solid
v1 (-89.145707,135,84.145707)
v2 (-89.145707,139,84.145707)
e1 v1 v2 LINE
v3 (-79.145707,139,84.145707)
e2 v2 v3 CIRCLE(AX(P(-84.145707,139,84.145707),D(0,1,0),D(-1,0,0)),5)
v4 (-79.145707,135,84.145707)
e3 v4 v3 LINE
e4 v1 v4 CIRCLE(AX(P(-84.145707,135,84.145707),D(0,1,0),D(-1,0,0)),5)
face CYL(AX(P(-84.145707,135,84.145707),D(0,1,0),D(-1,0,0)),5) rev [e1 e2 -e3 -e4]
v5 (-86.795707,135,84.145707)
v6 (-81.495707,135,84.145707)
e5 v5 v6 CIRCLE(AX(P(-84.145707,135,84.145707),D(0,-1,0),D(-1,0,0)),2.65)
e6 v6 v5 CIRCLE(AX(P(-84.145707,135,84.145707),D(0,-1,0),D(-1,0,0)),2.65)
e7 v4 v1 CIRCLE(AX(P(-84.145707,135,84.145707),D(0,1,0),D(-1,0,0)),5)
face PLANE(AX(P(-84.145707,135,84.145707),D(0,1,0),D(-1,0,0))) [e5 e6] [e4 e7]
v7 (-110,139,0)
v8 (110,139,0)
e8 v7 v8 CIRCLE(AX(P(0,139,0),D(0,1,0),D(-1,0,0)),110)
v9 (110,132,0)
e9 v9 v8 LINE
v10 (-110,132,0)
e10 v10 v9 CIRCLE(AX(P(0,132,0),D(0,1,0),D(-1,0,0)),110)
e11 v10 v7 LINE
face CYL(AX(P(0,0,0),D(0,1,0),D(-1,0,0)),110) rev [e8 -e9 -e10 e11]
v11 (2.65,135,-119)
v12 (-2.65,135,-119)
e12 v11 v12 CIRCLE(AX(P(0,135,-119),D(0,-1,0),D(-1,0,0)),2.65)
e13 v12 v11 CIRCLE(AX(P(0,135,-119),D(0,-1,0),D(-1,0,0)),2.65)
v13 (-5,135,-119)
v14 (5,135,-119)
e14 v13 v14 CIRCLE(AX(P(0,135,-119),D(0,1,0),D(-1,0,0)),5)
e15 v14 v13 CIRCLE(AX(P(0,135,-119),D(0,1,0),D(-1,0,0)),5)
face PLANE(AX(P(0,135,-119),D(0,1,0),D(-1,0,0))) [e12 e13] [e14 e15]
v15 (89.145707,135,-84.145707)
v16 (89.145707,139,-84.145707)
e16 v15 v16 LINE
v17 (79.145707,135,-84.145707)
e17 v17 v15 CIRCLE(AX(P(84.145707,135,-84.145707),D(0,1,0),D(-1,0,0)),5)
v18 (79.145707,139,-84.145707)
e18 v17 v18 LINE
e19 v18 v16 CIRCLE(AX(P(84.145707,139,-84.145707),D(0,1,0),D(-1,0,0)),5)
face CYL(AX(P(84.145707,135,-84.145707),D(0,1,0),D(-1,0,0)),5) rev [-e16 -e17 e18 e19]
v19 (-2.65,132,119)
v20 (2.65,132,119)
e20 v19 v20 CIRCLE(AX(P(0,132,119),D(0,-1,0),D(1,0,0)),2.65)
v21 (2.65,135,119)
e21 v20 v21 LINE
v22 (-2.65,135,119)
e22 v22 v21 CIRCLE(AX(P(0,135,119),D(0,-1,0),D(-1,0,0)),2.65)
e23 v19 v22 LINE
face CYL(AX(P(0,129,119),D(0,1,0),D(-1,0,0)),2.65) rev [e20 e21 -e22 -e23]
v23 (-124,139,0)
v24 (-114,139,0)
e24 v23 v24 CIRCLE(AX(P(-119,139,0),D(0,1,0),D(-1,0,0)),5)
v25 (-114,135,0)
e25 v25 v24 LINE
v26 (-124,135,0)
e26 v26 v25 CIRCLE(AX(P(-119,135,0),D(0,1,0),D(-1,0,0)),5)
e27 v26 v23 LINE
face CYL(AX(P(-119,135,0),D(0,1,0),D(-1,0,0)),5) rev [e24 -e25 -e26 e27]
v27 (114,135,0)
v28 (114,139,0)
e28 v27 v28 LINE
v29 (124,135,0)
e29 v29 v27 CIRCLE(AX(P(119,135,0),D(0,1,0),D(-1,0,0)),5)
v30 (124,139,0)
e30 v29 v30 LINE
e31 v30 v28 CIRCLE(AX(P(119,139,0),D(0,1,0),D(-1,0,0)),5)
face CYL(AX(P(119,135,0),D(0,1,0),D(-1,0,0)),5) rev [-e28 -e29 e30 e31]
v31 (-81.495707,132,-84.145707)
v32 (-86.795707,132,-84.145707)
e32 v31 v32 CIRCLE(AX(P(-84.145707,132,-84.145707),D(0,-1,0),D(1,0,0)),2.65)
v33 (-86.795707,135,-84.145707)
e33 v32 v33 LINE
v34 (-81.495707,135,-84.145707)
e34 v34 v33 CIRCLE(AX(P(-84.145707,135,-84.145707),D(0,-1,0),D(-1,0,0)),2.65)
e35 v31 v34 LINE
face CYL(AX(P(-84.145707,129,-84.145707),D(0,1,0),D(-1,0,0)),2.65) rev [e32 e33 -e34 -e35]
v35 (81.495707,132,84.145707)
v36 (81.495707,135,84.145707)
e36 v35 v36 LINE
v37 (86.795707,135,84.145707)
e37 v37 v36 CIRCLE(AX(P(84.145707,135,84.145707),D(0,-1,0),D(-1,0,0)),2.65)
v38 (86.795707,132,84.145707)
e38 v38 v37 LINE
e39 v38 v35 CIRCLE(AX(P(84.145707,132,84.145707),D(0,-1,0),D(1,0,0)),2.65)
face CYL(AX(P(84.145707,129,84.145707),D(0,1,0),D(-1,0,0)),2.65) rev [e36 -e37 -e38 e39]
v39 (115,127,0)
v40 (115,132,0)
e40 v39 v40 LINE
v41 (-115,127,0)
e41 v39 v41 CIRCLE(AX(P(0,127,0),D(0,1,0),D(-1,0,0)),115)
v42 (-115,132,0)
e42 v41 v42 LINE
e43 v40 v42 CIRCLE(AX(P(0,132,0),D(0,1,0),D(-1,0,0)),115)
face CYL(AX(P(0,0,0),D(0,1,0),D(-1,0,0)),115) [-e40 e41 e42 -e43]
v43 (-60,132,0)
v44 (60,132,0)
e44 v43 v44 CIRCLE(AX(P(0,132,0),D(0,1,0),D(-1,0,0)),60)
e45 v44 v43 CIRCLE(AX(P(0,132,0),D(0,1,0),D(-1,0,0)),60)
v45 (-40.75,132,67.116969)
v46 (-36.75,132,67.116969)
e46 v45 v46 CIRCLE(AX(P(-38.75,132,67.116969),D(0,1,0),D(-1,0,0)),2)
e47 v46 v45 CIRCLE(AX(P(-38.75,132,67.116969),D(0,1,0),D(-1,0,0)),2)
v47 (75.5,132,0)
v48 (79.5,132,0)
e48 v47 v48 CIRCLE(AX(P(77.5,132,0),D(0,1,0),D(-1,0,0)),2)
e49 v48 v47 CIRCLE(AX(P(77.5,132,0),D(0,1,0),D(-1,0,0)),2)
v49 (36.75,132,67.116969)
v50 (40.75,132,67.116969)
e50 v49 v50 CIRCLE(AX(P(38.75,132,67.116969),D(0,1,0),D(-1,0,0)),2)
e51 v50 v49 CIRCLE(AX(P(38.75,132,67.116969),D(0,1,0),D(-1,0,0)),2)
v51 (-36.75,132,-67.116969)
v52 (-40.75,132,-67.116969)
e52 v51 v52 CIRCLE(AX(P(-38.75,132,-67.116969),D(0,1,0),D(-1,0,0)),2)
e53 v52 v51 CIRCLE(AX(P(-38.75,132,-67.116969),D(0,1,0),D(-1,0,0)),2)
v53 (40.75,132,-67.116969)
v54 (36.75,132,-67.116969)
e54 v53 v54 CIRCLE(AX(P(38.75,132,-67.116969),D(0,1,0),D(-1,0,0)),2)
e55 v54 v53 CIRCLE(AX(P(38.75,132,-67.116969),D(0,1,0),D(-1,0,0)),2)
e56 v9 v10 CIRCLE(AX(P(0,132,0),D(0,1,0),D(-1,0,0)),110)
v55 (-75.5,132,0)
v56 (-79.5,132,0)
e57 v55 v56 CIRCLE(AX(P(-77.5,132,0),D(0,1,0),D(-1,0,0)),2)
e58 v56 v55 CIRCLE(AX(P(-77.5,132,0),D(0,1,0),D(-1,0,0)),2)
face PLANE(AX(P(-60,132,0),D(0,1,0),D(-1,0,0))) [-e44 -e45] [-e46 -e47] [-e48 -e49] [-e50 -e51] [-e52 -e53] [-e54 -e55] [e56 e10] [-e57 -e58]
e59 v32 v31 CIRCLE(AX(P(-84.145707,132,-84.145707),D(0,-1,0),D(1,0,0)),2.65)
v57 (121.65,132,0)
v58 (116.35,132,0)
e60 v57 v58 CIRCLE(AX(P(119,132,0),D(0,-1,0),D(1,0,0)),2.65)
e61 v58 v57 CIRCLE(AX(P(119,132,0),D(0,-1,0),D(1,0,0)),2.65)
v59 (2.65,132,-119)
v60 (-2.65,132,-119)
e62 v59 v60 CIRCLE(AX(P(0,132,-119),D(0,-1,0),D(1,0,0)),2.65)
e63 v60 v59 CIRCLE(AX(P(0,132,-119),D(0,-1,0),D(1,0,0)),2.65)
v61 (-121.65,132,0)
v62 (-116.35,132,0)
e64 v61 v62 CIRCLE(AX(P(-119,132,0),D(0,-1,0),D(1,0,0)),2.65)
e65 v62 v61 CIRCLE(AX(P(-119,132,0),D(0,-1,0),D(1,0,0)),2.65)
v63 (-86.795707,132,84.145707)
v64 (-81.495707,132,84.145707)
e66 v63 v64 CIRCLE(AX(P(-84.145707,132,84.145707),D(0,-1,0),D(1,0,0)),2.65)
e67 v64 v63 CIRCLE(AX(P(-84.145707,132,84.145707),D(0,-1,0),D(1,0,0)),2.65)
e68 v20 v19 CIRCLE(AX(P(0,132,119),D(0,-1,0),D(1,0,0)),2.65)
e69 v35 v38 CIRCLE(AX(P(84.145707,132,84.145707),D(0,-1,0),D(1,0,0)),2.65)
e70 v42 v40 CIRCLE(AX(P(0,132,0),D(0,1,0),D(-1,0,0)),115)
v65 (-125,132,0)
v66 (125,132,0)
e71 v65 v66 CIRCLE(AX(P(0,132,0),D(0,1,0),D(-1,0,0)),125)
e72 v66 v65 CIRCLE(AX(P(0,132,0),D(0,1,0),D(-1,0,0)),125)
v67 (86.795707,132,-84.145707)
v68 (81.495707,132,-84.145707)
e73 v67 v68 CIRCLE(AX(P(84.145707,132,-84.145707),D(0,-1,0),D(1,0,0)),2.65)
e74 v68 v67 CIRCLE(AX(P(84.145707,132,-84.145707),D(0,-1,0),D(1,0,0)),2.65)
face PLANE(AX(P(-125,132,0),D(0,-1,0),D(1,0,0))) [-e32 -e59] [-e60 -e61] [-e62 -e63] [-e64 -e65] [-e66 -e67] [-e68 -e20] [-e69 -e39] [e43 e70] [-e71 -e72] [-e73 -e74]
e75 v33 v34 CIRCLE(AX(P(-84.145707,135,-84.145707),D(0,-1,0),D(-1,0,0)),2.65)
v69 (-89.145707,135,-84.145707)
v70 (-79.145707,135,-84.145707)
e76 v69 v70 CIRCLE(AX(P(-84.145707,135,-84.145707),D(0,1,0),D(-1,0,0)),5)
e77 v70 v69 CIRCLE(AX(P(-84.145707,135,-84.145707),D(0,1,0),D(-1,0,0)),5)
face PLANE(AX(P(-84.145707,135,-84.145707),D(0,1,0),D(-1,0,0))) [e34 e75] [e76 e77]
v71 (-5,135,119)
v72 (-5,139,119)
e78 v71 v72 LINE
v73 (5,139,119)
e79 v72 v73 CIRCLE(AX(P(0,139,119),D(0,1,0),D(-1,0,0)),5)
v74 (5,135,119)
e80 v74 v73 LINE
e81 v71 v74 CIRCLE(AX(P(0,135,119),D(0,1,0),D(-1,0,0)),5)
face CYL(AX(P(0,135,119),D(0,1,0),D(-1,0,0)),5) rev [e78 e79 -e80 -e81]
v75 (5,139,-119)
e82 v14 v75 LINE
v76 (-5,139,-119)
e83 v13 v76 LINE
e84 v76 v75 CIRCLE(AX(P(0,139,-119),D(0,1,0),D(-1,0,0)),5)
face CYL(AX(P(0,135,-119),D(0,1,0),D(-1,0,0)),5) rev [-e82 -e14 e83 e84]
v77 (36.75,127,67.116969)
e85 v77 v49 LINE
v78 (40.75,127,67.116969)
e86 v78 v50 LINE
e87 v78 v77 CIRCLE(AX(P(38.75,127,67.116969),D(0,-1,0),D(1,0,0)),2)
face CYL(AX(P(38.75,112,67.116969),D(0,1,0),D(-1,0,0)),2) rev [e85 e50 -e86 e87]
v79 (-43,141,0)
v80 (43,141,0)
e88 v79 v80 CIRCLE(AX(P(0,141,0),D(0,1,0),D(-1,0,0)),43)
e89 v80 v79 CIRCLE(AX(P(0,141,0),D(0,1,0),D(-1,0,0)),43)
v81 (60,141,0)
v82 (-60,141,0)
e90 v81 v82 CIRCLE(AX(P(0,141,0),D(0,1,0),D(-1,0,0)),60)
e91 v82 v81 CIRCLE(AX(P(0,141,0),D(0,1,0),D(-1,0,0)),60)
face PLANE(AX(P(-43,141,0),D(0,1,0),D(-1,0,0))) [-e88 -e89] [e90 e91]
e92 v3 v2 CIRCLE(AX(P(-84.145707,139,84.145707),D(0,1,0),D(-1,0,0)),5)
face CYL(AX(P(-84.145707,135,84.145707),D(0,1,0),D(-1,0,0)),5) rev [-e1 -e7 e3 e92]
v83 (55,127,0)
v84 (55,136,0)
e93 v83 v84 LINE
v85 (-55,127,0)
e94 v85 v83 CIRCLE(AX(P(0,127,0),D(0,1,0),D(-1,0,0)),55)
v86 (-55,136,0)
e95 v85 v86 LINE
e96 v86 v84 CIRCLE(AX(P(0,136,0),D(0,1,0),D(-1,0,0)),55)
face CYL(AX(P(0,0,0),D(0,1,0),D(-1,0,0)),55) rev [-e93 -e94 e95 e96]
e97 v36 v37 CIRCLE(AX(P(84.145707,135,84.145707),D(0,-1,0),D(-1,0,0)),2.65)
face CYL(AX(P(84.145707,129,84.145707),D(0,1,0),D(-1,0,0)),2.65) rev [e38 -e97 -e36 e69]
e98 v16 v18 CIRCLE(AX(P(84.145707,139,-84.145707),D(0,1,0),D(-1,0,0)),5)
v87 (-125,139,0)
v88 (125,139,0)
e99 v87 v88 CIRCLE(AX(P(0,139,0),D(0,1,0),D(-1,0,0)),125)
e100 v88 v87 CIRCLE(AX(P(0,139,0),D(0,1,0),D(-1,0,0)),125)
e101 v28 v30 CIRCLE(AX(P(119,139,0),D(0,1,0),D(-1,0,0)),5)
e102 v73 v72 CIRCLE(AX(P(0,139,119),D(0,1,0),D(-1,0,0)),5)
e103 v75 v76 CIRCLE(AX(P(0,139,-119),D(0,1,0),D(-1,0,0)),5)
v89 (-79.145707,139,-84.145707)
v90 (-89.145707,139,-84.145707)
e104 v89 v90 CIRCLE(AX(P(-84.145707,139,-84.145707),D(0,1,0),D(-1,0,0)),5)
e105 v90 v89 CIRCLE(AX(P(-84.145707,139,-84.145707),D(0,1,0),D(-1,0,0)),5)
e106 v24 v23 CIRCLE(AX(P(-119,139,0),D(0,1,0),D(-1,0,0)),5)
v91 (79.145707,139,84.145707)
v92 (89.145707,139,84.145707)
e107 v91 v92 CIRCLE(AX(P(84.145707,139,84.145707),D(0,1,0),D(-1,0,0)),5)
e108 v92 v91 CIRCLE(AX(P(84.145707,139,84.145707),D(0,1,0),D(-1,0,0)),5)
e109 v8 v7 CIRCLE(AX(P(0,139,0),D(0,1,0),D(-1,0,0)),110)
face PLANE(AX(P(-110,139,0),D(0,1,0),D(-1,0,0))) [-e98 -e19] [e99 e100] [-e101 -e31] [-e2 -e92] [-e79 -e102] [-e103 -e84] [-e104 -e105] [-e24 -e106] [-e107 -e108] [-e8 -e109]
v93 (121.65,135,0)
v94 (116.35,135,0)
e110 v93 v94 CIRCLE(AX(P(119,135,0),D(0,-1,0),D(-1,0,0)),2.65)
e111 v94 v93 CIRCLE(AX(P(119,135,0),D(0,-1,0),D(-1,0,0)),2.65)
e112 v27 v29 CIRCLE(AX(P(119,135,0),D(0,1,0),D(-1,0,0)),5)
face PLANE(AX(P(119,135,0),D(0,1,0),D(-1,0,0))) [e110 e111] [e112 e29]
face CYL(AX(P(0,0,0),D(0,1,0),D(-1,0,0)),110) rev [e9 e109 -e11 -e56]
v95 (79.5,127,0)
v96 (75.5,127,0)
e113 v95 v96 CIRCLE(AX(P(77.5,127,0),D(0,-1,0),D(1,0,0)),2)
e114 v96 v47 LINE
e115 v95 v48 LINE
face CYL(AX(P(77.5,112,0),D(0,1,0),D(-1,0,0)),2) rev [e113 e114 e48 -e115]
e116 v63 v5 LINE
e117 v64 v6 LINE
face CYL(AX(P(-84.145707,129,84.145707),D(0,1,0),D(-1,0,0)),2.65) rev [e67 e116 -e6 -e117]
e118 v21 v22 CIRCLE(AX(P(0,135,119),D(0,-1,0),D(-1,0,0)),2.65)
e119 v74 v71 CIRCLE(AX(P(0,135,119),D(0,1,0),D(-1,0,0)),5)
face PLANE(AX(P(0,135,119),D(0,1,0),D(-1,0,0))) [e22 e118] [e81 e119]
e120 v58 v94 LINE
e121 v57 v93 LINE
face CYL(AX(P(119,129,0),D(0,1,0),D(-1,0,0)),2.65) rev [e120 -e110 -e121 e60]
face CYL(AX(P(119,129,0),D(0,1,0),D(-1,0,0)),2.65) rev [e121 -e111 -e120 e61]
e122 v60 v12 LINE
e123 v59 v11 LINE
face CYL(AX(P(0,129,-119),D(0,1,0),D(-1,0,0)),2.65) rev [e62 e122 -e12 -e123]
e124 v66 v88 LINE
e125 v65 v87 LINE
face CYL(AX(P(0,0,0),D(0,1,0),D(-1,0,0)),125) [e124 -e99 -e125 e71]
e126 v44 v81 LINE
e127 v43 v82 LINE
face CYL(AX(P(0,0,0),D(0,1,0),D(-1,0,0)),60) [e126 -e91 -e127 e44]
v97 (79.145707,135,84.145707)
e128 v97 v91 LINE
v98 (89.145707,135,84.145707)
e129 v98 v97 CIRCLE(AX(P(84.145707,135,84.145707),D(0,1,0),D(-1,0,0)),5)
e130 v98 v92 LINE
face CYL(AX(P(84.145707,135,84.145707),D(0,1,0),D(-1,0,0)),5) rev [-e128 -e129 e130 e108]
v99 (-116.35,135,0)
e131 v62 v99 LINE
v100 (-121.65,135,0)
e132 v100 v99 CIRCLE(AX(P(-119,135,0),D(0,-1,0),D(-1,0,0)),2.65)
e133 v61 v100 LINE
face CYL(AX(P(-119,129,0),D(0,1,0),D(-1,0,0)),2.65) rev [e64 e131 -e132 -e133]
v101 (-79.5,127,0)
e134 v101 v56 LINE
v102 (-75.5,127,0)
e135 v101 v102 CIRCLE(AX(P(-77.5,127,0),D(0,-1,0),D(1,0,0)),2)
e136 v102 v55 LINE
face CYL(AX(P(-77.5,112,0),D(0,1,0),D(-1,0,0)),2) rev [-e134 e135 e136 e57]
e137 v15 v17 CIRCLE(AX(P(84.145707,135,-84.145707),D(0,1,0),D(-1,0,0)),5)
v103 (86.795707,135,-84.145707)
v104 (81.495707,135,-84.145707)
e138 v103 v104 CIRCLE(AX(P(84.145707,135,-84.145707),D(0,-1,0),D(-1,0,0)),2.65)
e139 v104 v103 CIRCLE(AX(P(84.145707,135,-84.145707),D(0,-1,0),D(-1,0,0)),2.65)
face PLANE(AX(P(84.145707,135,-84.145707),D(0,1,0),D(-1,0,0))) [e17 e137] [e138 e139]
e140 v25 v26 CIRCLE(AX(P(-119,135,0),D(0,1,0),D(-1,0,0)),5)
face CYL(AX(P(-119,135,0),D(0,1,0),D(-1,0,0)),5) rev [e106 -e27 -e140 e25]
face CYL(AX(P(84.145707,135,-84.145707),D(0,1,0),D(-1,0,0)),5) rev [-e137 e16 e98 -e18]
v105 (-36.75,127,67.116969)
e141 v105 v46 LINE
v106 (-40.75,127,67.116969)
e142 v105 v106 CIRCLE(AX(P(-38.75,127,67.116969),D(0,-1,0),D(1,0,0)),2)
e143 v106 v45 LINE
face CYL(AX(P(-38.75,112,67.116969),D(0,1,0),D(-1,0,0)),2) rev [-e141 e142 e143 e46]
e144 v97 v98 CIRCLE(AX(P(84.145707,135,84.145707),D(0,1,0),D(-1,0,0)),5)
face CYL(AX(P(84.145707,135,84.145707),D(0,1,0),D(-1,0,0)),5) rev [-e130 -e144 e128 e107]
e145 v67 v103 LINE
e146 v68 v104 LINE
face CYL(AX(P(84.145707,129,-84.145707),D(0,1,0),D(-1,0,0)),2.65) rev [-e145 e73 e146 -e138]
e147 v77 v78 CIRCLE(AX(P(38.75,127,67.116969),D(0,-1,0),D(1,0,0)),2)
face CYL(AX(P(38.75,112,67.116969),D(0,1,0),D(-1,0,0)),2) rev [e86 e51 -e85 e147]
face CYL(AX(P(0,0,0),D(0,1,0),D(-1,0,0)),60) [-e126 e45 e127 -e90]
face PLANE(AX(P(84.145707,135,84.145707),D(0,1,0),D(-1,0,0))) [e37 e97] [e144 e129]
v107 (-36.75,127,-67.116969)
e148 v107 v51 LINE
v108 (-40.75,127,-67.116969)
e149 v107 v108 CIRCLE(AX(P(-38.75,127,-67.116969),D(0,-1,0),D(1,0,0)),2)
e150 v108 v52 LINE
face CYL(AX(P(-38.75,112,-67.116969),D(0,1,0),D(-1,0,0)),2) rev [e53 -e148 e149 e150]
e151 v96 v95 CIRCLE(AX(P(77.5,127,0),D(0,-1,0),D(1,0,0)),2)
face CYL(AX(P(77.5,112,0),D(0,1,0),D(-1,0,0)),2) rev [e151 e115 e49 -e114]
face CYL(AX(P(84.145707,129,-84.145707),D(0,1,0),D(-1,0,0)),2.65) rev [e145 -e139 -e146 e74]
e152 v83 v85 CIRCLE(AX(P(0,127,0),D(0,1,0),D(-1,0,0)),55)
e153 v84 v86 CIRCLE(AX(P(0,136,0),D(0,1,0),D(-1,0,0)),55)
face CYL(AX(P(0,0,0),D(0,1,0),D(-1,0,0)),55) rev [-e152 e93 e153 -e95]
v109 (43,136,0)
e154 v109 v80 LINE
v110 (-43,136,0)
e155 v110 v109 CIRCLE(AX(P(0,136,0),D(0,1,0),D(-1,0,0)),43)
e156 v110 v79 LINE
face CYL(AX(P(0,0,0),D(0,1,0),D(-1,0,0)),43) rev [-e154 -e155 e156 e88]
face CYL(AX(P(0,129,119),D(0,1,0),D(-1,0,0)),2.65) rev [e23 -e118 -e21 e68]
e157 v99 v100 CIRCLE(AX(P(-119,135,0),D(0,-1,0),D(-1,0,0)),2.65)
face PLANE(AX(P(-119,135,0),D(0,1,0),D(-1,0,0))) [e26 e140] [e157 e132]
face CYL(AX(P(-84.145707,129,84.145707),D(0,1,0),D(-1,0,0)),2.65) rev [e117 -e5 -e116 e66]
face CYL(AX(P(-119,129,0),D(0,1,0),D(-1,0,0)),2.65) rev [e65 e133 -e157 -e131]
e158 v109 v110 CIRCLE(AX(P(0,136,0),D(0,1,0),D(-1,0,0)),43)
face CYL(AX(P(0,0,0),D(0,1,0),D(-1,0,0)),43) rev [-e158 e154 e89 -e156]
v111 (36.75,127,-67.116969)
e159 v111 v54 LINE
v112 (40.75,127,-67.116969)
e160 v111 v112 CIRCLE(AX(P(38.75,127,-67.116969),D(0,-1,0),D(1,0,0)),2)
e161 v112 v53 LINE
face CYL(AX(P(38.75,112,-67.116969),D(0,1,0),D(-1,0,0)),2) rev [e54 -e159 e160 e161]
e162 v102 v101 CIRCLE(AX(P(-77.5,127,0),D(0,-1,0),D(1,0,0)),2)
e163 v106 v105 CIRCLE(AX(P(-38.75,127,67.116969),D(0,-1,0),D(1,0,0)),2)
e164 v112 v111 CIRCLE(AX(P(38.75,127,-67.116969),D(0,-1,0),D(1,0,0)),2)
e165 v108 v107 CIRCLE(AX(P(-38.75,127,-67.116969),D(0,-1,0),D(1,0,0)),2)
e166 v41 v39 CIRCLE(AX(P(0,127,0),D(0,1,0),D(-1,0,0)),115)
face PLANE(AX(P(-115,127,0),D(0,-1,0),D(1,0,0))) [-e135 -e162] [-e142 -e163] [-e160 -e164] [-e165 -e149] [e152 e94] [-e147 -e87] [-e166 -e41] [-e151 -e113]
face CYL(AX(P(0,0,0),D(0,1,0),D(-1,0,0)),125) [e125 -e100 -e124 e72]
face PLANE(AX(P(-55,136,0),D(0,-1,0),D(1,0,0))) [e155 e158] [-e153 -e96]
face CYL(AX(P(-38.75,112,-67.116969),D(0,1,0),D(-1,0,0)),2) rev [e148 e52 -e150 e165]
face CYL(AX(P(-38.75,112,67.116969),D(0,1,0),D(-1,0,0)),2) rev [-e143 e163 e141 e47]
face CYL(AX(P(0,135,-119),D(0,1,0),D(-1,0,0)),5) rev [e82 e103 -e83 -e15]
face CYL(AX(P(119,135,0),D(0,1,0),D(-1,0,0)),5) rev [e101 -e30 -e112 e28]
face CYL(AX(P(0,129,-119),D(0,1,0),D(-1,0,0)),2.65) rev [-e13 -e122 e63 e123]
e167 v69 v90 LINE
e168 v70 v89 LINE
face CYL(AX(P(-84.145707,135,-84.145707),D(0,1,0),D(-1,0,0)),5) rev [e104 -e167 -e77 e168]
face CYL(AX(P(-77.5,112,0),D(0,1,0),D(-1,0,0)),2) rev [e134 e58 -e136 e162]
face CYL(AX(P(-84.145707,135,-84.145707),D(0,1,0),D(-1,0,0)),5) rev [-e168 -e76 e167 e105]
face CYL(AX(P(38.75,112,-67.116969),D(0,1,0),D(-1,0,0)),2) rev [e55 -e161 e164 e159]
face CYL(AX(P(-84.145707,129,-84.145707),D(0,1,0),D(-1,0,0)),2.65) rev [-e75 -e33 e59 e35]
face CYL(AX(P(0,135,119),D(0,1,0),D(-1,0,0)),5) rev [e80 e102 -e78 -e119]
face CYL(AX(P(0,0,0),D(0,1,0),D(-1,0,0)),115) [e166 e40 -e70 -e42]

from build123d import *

# Parameters (mm, degrees)
SKETCH2_R          = 2.65
CUT_EXTRUDE1_DEPTH = 10
SKETCH3_R          = 5
CUT_EXTRUDE3_DEPTH = 4
SKETCH4_R          = 2
CUT_EXTRUDE4_DEPTH = 20


with BuildPart() as part:
    # Sketch1 → Revolve1 (revolve)
    with BuildSketch(Plane.XY):
        Polygon((-125, 132), (-115, 132), (-115, 127), (-55, 127), (-55, 136), (-43, 136), (-43, 141), (-60, 141), (-60, 132), (-110, 132), (-110, 139), (-125, 139), align=None)
    revolve(axis=Axis((0, 0, 0), (0, -1, 0)))

    # Sketch2 → Cut-Extrude1 (cut)
    with BuildSketch(Plane(origin=(0, 139, 0), x_dir=(1, 0, 0), z_dir=(0, 1, 0))):
        with Locations(Location((0, 119, 0), (0, 0, 180))):
            Circle(SKETCH2_R)
        with Locations(Location((84.145706961, 84.145706961, 0), (0, 0, 180))):
            Circle(SKETCH2_R)
        with Locations(Location((119, 0, 0), (0, 0, 180))):
            Circle(SKETCH2_R)
        with Locations(Location((84.145706961, -84.145706961, 0), (0, 0, 180))):
            Circle(SKETCH2_R)
        with Locations(Location((0, -119, 0), (0, 0, 180))):
            Circle(SKETCH2_R)
        with Locations(Location((-84.145706961, -84.145706961, 0), (0, 0, 180))):
            Circle(SKETCH2_R)
        with Locations(Location((-119, 0, 0), (0, 0, 180))):
            Circle(SKETCH2_R)
        with Locations(Location((-84.145706961, 84.145706961, 0), (0, 0, 180))):
            Circle(SKETCH2_R)
    extrude(amount=-CUT_EXTRUDE1_DEPTH, mode=Mode.SUBTRACT)

    # Sketch3 → Cut-Extrude3 (cut)
    with BuildSketch(Plane(origin=(0, 139, 0), x_dir=(1, 0, 0), z_dir=(0, 1, 0))):
        with Locations(Location((0, 119, 0), (0, 0, 180))):
            Circle(SKETCH3_R)
        with Locations(Location((84.145706961, 84.145706961, 0), (0, 0, 180))):
            Circle(SKETCH3_R)
        with Locations(Location((119, 0, 0), (0, 0, 180))):
            Circle(SKETCH3_R)
        with Locations(Location((84.145706961, -84.145706961, 0), (0, 0, 180))):
            Circle(SKETCH3_R)
        with Locations(Location((0, -119, 0), (0, 0, 180))):
            Circle(SKETCH3_R)
        with Locations(Location((-84.145706961, -84.145706961, 0), (0, 0, 180))):
            Circle(SKETCH3_R)
        with Locations(Location((-119, 0, 0), (0, 0, 180))):
            Circle(SKETCH3_R)
        with Locations(Location((-84.145706961, 84.145706961, 0), (0, 0, 180))):
            Circle(SKETCH3_R)
    extrude(amount=-CUT_EXTRUDE3_DEPTH, mode=Mode.SUBTRACT)

    # Sketch4 → Cut-Extrude4 (cut)
    with BuildSketch(Plane(origin=(0, 132, 0), x_dir=(1, 0, 0), z_dir=(0, 1, 0))):
        with Locations(Location((77.5, 0, 0), (0, 0, 180))):
            Circle(SKETCH4_R)
        with Locations(Location((38.75, -67.116968793, 0), (0, 0, 180))):
            Circle(SKETCH4_R)
        with Locations(Location((-38.75, -67.116968793, 0), (0, 0, 180))):
            Circle(SKETCH4_R)
        with Locations(Location((-77.5, 0, 0), (0, 0, 180))):
            Circle(SKETCH4_R)
        with Locations(Location((-38.75, 67.116968793, 0), (0, 0, 180))):
            Circle(SKETCH4_R)
        with Locations(Location((38.75, 67.116968793, 0), (0, 0, 180))):
            Circle(SKETCH4_R)
    extrude(amount=-CUT_EXTRUDE4_DEPTH, mode=Mode.SUBTRACT)


solid = part.part
